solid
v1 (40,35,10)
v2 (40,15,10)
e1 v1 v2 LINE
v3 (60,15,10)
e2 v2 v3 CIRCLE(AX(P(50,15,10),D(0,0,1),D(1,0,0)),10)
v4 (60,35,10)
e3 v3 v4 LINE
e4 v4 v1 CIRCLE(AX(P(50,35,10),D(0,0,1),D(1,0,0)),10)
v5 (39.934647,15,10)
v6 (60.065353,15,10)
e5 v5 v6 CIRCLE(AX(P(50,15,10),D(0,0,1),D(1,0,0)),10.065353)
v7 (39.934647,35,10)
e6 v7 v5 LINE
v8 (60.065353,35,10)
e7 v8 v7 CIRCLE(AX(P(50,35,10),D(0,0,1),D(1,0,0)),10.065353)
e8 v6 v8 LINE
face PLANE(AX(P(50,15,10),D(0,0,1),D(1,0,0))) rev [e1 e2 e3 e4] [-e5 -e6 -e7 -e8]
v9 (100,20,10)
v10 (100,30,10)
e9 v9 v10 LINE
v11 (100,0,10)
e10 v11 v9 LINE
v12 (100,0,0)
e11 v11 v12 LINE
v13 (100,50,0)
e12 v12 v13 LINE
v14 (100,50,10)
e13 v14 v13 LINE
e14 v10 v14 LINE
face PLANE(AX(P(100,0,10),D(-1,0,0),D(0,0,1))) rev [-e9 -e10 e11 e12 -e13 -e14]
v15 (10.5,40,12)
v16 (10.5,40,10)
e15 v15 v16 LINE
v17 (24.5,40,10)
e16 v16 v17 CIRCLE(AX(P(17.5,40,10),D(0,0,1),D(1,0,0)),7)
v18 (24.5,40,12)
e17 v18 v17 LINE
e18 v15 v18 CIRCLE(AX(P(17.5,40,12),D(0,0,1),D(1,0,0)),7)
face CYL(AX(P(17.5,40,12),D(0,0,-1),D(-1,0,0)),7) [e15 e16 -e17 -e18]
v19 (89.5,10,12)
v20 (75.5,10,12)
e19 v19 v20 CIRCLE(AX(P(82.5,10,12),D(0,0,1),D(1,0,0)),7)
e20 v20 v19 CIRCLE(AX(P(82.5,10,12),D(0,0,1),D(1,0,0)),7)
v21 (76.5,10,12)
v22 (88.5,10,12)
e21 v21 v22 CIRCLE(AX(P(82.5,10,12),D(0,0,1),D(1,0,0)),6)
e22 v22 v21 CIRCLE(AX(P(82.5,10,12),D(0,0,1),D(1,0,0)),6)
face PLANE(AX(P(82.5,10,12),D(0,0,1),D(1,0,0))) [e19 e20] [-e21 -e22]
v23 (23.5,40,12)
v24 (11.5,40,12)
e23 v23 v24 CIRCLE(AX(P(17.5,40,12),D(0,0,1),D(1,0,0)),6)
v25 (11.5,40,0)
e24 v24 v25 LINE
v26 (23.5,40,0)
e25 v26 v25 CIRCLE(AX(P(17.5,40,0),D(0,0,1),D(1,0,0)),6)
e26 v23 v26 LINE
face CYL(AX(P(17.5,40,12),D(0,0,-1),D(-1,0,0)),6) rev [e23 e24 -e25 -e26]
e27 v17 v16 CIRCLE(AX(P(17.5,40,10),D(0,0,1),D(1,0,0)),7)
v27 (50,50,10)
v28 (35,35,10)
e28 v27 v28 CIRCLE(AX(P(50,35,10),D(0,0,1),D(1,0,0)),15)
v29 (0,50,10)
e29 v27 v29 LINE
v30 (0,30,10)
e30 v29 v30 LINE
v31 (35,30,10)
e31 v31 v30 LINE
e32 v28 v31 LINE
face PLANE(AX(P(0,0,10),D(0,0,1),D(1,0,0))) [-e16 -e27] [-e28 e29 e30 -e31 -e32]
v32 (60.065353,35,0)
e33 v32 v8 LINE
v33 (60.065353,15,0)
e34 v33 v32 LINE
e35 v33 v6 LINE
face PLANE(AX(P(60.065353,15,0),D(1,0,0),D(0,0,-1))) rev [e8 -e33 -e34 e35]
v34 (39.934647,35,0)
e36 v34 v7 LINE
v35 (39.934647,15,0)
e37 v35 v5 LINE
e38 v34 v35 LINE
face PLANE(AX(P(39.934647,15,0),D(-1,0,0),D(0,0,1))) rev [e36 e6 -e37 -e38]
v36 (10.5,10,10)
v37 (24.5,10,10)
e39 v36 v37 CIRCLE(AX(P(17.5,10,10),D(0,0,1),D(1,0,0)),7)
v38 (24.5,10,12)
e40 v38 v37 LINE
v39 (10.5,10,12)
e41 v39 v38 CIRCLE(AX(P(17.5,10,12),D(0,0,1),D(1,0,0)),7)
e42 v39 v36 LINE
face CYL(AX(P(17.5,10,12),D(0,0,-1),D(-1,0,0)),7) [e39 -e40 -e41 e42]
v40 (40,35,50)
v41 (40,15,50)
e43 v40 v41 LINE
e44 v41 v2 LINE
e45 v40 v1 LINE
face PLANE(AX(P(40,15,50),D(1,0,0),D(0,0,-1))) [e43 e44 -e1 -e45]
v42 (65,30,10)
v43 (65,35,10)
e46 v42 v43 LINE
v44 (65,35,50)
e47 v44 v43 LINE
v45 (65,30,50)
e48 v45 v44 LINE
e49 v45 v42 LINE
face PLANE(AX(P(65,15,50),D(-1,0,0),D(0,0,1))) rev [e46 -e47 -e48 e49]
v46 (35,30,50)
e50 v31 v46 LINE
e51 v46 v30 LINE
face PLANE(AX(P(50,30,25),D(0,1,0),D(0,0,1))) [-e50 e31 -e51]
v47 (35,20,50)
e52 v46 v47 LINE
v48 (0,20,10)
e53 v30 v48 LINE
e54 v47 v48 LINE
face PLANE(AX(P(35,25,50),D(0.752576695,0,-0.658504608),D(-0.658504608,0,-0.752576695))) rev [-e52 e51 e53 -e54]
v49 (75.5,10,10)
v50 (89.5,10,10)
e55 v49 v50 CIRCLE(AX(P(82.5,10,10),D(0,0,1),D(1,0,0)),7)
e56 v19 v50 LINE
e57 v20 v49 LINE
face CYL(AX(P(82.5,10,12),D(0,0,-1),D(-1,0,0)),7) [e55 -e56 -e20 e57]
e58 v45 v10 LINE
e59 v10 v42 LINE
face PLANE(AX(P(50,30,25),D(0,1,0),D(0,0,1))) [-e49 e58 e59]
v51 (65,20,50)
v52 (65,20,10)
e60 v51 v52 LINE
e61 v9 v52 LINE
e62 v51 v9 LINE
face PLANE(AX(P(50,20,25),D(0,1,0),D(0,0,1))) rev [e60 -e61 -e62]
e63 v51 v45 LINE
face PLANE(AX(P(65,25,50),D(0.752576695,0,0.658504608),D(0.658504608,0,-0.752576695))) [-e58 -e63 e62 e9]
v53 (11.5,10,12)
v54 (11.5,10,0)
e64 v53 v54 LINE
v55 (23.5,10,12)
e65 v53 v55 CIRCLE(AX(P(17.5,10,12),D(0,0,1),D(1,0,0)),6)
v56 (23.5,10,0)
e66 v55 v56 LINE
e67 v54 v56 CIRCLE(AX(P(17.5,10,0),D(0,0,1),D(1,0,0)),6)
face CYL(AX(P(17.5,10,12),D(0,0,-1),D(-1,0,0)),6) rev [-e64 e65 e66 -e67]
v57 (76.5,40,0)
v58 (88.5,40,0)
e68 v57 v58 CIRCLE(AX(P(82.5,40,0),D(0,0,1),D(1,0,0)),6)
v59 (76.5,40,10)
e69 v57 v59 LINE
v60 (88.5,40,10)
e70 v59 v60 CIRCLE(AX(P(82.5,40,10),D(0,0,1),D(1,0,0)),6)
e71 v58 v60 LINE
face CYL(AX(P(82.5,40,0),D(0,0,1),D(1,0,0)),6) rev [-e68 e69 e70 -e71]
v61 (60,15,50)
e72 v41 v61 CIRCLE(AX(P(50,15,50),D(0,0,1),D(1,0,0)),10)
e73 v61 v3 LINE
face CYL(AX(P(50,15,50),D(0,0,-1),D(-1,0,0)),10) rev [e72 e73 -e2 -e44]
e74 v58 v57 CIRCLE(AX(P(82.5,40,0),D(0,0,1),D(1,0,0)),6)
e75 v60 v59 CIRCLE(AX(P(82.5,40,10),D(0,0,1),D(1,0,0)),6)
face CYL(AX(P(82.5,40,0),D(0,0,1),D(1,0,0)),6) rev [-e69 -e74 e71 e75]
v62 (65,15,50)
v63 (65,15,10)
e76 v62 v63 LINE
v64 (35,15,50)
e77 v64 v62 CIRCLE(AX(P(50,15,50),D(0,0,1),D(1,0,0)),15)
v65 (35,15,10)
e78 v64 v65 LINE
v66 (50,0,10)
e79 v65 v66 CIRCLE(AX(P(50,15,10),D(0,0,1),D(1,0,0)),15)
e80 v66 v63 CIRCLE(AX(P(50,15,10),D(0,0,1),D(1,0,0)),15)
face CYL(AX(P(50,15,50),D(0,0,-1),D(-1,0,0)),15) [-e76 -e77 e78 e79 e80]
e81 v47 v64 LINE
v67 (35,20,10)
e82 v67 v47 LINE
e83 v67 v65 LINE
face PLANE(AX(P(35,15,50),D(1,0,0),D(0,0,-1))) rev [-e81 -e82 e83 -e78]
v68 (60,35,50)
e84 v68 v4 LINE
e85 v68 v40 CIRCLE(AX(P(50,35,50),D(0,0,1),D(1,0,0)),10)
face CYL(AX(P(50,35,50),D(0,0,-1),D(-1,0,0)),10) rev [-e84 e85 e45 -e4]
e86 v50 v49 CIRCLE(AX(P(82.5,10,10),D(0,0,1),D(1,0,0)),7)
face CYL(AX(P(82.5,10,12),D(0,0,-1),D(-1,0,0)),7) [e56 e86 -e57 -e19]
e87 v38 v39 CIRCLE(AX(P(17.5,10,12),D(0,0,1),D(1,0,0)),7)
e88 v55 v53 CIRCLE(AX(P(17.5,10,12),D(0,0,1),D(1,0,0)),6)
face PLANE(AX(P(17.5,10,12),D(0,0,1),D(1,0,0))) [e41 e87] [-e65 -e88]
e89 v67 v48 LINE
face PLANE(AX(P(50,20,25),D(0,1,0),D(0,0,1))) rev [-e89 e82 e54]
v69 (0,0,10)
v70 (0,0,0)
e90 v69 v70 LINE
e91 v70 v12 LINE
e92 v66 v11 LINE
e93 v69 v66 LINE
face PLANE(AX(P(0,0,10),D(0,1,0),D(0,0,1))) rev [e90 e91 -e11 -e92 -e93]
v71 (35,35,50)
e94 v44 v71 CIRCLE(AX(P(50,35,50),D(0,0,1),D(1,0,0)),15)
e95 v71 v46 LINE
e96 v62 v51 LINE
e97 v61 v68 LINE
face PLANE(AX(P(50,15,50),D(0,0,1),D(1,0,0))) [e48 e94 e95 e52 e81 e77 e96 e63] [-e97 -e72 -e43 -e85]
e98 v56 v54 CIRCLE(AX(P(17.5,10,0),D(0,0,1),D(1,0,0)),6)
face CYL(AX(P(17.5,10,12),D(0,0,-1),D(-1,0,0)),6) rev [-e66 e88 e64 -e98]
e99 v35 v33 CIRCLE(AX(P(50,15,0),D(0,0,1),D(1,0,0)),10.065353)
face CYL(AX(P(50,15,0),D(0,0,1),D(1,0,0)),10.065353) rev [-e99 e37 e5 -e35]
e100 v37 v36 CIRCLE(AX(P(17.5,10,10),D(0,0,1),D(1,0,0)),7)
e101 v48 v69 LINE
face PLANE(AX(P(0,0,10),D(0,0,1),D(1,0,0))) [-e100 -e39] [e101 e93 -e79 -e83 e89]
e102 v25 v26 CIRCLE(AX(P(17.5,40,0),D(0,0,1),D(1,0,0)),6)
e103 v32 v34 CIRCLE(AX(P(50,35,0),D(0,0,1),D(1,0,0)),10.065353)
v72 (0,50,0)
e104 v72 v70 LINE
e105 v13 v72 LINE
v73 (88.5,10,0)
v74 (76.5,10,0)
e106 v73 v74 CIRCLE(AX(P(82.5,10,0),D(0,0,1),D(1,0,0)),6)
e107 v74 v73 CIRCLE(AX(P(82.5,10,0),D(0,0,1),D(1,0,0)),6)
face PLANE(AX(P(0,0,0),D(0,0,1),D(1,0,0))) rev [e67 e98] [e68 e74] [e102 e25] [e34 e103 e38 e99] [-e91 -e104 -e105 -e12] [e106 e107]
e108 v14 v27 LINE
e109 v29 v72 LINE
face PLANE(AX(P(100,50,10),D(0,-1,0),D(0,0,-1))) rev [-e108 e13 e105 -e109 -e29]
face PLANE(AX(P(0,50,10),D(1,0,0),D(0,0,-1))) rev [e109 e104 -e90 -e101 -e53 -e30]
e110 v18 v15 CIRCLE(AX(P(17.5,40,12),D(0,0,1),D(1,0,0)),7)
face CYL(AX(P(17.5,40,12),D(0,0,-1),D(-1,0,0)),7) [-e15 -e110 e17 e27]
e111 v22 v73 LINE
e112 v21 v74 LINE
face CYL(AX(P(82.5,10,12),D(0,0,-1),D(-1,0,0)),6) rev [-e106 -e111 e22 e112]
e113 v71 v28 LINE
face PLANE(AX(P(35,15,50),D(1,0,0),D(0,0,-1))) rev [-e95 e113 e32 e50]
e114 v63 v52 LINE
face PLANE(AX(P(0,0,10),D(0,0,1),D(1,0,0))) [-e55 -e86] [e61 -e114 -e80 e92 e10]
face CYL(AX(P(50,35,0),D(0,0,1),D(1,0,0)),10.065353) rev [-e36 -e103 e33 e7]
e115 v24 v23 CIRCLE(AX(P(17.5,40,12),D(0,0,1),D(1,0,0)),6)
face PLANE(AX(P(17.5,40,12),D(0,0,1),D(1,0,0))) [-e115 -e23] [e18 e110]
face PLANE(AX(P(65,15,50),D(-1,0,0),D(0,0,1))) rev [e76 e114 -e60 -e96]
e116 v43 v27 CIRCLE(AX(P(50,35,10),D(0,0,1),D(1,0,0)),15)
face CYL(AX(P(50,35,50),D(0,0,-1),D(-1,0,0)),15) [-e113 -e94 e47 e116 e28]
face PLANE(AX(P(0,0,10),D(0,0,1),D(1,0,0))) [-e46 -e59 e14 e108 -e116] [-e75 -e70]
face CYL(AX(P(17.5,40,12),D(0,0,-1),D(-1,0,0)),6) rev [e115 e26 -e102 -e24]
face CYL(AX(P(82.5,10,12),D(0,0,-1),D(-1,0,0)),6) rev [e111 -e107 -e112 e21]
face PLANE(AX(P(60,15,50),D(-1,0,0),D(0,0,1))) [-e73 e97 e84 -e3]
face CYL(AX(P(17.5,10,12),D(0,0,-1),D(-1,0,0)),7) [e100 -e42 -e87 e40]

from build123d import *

# Parameters (mm, degrees)
BASE_PLATE_SKETCH_W         = 100
BASE_PLATE_SKETCH_H         = 50
BASE_PLATE_100X50X10_DEPTH  = 10
OVAL_BOSS_DEPTH             = 40
SUPPORT_RIB_1_REACH         = 116.564
SUPPORT_RIB_1_SKETCH_WALL_W = 284.279513812
SUPPORT_RIB_1_SKETCH_WALL_H = 10
SUPPORT_RIB_2_REACH         = 116.564
SUPPORT_RIB_2_SKETCH_WALL_W = 284.279513812
SUPPORT_RIB_2_SKETCH_WALL_H = 10
RAISED_PADS_SKETCH_R        = 7
RAISED_PADS_SKETCH_R_2      = 6
RAISED_PADS_2MM_DEPTH       = 2
MOUNTING_HOLE_1_SKETCH_R    = 6
MOUNTING_HOLE_1_DEPTH       = 119.74342087
MOUNTING_HOLE_2_SKETCH_R    = 6
MOUNTING_HOLE_2_DEPTH       = 119.74342087
MOUNTING_HOLE_3_SKETCH_R    = 6
MOUNTING_HOLE_3_DEPTH       = 119.084715353
MOUNTING_HOLE_4_SKETCH_R    = 6
MOUNTING_HOLE_4_DEPTH       = 119.74342087
BOSS_BORE_DEPTH             = 119.74342087


with BuildPart() as part:
    # Base Plate Sketch → Base Plate 100x50x10 (new body)
    with BuildSketch(Plane.XY):
        with Locations((50, 25)):
            Rectangle(BASE_PLATE_SKETCH_W, BASE_PLATE_SKETCH_H)
    extrude(amount=BASE_PLATE_100X50X10_DEPTH)

    # Oval Boss Sketch → Oval Boss (add)
    with BuildSketch(Plane.XY.offset(10)):
        with BuildLine():
            Line((35, 15), (35, 35))
            ThreePointArc((35, 35), (50, 50), (65, 35))
            Line((65, 35), (65, 15))
            ThreePointArc((65, 15), (50, 0), (35, 15))
        make_face()
        with BuildLine():
            Line((40, 15), (40, 35))
            ThreePointArc((40, 35), (50, 45), (60, 35))
            Line((60, 35), (60, 15))
            ThreePointArc((60, 15), (50, 5), (40, 15))
        make_face(mode=Mode.SUBTRACT)
    extrude(amount=OVAL_BOSS_DEPTH)

    # Support Rib 1 Sketch wall → Support Rib 1 (add, up to next)
    with BuildSketch(Plane(origin=(82.5, 25, 30), x_dir=(0.658504607869, 0, -0.752576694707), z_dir=(-0.752576694707, 0, -0.658504607869)), mode=Mode.PRIVATE) as support_rib_1_sk1:
        Rectangle(SUPPORT_RIB_1_SKETCH_WALL_W, SUPPORT_RIB_1_SKETCH_WALL_H)
    support_rib_1_tool1 = extrude(support_rib_1_sk1.sketch, amount=SUPPORT_RIB_1_REACH, mode=Mode.PRIVATE) - part.part
    add(support_rib_1_tool1.solids().sort_by_distance((82.5, 25, 30))[0])

    # Support Rib 2 Sketch wall → Support Rib 2 (add, up to next)
    with BuildSketch(Plane(origin=(17.5, 25, 30), x_dir=(-0.658504607869, 0, -0.752576694707), z_dir=(-0.752576694707, 0, 0.658504607869)), mode=Mode.PRIVATE) as support_rib_2_sk1:
        Rectangle(SUPPORT_RIB_2_SKETCH_WALL_W, SUPPORT_RIB_2_SKETCH_WALL_H)
    support_rib_2_tool1 = extrude(support_rib_2_sk1.sketch, amount=-SUPPORT_RIB_2_REACH, mode=Mode.PRIVATE) - part.part
    add(support_rib_2_tool1.solids().sort_by_distance((17.5, 25, 30))[0])

    # Raised Pads Sketch → Raised Pads 2mm (add)
    # profile 1 of 4: a face of its own
    with BuildSketch(Plane.XY.offset(10)):
        with Locations((17.5, 10)):
            Circle(RAISED_PADS_SKETCH_R)
        with Locations((17.5, 10)):
            Circle(RAISED_PADS_SKETCH_R_2, mode=Mode.SUBTRACT)
    # profile 2 of 4: a face of its own
    with BuildSketch(Plane.XY.offset(10)):
        with Locations((82.5, 10)):
            Circle(RAISED_PADS_SKETCH_R)
        with Locations((82.5, 10)):
            Circle(RAISED_PADS_SKETCH_R_2, mode=Mode.SUBTRACT)
    # profile 3 of 4: a face of its own
    with BuildSketch(Plane.XY.offset(10)):
        with Locations((17.5, 40)):
            Circle(RAISED_PADS_SKETCH_R)
        with Locations((17.5, 40)):
            Circle(RAISED_PADS_SKETCH_R_2, mode=Mode.SUBTRACT)
    # profile 4 of 4: a face of its own
    with BuildSketch(Plane.XY.offset(10)):
        with Locations((82.5, 40)):
            Circle(RAISED_PADS_SKETCH_R_2)
    extrude(amount=RAISED_PADS_2MM_DEPTH)

    # Mounting Hole 1 Sketch → Mounting Hole 1 (cut, through all)
    with BuildSketch(Plane.XY.offset(10)):
        with Locations((17.5, 40)):
            Circle(MOUNTING_HOLE_1_SKETCH_R)
    extrude(amount=-MOUNTING_HOLE_1_DEPTH, mode=Mode.SUBTRACT)

    # Mounting Hole 2 Sketch → Mounting Hole 2 (cut, through all)
    with BuildSketch(Plane.XY.offset(10)):
        with Locations((17.5, 10)):
            Circle(MOUNTING_HOLE_2_SKETCH_R)
    extrude(amount=-MOUNTING_HOLE_2_DEPTH, mode=Mode.SUBTRACT)

    # Mounting Hole 3 Sketch → Mounting Hole 3 (cut, through all)
    with BuildSketch(Plane.XY.offset(12)):
        with Locations((82.5, 40)):
            Circle(MOUNTING_HOLE_3_SKETCH_R)
    extrude(amount=-MOUNTING_HOLE_3_DEPTH, mode=Mode.SUBTRACT)

    # Mounting Hole 4 Sketch → Mounting Hole 4 (cut, through all)
    with BuildSketch(Plane.XY.offset(10)):
        with Locations((82.5, 10)):
            Circle(MOUNTING_HOLE_4_SKETCH_R)
    extrude(amount=-MOUNTING_HOLE_4_DEPTH, mode=Mode.SUBTRACT)

    # Boss Bore Sketch → Boss Bore (cut, through all)
    with BuildSketch(Plane.XY.offset(10)):
        with BuildLine():
            Line((39.934647115, 15), (39.934647115, 35))
            ThreePointArc((39.934647115, 35), (50, 45.065352885), (60.065352885, 35))
            Line((60.065352885, 35), (60.065352885, 15))
            ThreePointArc((60.065352885, 15), (50, 4.934647115), (39.934647115, 15))
        make_face()
    extrude(amount=-BOSS_BORE_DEPTH, mode=Mode.SUBTRACT)


solid = part.part
